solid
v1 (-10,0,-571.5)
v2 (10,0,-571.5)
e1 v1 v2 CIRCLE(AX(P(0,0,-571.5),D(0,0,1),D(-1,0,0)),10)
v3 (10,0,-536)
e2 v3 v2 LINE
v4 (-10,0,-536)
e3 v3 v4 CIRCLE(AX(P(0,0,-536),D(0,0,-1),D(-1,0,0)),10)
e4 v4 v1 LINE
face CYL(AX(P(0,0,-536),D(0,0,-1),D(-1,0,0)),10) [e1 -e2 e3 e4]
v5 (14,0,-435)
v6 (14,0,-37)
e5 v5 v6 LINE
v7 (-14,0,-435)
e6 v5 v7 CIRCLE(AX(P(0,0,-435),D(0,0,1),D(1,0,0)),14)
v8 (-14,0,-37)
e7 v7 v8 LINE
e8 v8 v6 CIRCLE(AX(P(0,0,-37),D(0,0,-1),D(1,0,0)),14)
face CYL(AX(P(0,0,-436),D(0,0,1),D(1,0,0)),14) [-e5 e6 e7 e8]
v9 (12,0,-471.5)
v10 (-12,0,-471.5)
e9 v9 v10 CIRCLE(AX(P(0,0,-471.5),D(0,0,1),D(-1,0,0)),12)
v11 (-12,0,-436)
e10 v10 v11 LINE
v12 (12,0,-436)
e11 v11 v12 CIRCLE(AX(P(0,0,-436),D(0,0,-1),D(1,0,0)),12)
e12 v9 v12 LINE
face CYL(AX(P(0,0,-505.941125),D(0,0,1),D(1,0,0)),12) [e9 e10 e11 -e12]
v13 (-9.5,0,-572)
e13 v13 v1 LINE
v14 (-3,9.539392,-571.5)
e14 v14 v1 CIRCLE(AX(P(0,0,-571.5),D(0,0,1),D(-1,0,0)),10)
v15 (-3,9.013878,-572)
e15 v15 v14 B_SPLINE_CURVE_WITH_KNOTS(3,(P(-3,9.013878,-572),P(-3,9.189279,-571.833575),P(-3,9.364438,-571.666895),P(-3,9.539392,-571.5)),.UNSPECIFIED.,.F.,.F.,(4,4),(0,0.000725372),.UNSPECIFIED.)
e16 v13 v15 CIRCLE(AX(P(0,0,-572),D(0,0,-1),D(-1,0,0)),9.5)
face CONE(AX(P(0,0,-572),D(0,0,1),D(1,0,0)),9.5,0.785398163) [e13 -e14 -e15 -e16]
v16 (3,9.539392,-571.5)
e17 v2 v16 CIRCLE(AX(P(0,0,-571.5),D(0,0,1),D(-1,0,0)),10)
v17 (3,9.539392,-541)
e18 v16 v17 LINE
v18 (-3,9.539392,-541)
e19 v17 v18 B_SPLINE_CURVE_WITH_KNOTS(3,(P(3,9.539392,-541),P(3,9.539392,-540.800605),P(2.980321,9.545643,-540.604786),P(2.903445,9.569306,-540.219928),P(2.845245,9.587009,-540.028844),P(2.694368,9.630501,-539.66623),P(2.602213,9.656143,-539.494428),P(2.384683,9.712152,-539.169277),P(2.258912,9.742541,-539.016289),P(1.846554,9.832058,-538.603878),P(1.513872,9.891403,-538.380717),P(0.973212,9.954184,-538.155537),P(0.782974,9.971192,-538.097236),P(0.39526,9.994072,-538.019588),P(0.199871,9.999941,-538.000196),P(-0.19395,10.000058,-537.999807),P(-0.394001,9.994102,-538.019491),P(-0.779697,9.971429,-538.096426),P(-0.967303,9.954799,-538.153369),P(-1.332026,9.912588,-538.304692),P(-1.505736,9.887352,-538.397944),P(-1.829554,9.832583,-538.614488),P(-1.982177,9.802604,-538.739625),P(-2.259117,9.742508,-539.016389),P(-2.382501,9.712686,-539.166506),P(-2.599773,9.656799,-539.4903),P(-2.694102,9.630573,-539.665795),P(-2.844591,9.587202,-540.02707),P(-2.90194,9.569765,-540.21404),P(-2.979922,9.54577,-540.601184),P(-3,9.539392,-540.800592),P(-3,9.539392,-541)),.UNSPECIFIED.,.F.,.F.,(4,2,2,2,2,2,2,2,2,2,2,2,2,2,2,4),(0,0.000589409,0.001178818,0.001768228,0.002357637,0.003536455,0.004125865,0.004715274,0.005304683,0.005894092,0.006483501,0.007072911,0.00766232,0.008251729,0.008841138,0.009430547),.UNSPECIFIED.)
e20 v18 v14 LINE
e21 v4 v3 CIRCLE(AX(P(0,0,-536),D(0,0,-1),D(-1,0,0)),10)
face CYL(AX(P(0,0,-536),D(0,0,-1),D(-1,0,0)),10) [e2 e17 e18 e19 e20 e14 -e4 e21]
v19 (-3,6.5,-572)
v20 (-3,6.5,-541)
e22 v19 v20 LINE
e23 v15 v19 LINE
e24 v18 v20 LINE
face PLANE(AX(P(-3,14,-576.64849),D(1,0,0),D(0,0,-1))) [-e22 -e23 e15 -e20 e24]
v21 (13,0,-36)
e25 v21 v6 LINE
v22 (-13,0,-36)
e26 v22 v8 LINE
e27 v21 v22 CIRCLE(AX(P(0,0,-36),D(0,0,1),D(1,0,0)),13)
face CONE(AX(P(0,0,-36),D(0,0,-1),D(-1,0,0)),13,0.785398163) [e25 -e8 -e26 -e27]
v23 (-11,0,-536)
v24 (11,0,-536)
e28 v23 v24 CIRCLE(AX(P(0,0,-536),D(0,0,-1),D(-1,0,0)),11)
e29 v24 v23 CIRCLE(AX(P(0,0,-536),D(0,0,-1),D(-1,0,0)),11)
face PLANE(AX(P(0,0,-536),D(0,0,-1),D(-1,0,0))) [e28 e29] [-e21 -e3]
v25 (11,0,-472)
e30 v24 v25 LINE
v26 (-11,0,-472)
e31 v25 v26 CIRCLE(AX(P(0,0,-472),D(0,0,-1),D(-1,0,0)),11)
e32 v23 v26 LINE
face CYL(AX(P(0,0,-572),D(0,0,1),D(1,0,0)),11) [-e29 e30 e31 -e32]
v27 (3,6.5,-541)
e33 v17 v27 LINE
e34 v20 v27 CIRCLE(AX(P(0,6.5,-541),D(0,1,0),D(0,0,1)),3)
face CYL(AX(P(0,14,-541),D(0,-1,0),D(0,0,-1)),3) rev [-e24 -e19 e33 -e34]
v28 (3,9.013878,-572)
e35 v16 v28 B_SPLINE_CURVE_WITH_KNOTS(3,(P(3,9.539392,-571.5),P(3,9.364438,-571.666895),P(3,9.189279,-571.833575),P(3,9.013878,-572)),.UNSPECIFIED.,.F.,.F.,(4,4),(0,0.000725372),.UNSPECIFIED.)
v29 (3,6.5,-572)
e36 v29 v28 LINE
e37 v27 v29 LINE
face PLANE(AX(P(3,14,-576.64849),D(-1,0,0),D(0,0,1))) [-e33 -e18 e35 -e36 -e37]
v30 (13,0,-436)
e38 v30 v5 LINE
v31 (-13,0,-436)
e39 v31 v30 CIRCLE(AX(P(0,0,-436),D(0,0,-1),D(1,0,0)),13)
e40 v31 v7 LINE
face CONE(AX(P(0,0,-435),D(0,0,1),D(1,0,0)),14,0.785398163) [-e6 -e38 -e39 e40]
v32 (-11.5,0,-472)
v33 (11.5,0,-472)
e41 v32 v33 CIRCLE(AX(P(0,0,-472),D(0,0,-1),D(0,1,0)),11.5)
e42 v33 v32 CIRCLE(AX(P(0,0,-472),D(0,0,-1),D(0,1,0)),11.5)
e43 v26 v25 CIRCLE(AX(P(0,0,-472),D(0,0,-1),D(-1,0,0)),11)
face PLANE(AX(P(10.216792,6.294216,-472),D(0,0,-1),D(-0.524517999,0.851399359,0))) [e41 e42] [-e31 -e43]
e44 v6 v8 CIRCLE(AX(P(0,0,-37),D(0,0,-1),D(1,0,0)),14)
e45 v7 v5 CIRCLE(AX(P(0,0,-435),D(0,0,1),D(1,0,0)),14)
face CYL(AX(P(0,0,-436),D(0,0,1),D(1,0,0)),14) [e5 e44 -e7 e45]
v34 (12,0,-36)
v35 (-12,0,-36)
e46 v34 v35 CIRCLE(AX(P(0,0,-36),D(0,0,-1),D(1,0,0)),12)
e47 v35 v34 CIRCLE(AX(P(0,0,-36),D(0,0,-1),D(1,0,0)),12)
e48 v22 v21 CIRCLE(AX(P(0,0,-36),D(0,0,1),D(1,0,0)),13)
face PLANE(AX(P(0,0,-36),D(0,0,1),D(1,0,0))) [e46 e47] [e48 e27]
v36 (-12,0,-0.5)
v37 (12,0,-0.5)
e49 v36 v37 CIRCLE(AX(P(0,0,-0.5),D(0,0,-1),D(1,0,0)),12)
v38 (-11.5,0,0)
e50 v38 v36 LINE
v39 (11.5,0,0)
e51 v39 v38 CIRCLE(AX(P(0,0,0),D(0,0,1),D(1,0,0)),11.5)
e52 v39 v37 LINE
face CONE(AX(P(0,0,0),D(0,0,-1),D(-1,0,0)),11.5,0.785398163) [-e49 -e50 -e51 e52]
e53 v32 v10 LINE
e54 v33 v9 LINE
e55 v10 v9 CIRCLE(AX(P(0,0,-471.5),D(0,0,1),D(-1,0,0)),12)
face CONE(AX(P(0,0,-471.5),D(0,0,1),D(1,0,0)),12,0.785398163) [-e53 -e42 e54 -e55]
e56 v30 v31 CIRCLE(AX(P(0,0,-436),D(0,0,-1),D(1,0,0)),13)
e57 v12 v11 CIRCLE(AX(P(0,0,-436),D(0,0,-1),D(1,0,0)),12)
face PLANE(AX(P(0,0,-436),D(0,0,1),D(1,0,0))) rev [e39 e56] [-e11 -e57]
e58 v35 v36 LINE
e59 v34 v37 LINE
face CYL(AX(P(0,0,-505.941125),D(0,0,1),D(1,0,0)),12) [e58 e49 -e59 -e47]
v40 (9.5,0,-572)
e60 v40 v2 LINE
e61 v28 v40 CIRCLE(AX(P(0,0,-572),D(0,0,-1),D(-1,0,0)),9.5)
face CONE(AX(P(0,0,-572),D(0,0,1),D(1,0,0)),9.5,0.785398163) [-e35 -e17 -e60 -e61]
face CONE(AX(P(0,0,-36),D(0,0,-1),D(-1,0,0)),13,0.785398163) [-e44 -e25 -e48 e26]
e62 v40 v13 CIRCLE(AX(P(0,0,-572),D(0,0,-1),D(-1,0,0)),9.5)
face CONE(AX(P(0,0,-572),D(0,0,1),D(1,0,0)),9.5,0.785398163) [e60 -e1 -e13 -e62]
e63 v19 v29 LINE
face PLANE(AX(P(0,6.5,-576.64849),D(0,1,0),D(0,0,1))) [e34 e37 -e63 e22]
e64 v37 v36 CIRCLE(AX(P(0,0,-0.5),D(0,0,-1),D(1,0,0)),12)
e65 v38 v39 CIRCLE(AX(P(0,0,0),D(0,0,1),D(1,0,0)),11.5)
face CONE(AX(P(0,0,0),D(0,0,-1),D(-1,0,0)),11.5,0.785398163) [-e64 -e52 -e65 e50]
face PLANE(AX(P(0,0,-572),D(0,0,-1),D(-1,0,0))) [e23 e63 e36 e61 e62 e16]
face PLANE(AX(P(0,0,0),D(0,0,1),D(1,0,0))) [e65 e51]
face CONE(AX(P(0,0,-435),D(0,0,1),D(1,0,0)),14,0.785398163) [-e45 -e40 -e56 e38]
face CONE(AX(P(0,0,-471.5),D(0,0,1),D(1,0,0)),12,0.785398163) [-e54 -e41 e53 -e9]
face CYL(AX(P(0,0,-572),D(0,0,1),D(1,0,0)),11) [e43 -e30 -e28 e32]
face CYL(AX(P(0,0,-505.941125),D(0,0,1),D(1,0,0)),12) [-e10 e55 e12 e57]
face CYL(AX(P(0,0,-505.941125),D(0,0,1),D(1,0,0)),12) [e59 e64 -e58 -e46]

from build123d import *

# Parameters (mm, degrees)
SKETCH1_R           = 12
BOSS_EXTRUDE1_DEPTH = 472
SKETCH2_R           = 11
BOSS_EXTRUDE2_DEPTH = 100
SKETCH4_R           = 14
BOSS_EXTRUDE3_DEPTH = 400
CHAMFER1_SIZE       = 1
CHAMFER2_SIZE       = 0.5
CHAMFER3_SIZE       = 0.5
SKETCH5_R           = 20
SKETCH5_R_2         = 10
CUT_EXTRUDE1_DEPTH  = 36
CUT_EXTRUDE2_DEPTH  = 573.538426658
CHAMFER4_SIZE       = 0.5


with BuildPart() as part:
    # Sketch1 → Boss-Extrude1 (new body)
    with BuildSketch(Plane.XY):
        Circle(SKETCH1_R)
    extrude(amount=-BOSS_EXTRUDE1_DEPTH)

    # Sketch2 → Boss-Extrude2 (add)
    with BuildSketch(Plane(origin=(0, 0, -472), x_dir=(-1, 0, 0), z_dir=(0, 0, -1))):
        Circle(SKETCH2_R)
    extrude(amount=BOSS_EXTRUDE2_DEPTH)

    # Sketch4 → Boss-Extrude3 (add)
    with BuildSketch(Plane.XY.offset(-36)):
        Circle(SKETCH4_R)
    extrude(amount=-BOSS_EXTRUDE3_DEPTH)

    # Chamfer1
    chamfer1_edges = [part.edges().sort_by_distance(p)[0] for p in [
        (-14, 0, -36),
        (-14, 0, -436),
    ]]
    chamfer(chamfer1_edges, length=CHAMFER1_SIZE)

    # Chamfer2
    chamfer2_edges = [part.edges().sort_by_distance(p)[0] for p in [
        (-12, 0, 0),
    ]]
    chamfer(chamfer2_edges, length=CHAMFER2_SIZE)

    # Chamfer3
    chamfer3_edges = [part.edges().sort_by_distance(p)[0] for p in [
        (-12, 0, -472),
    ]]
    chamfer(chamfer3_edges, length=CHAMFER3_SIZE)

    # Sketch5 → Cut-Extrude1 (cut)
    with BuildSketch(Plane(origin=(0, 0, -572), x_dir=(-1, 0, 0), z_dir=(0, 0, -1))):
        Circle(SKETCH5_R)
        Circle(SKETCH5_R_2, mode=Mode.SUBTRACT)
    extrude(amount=-CUT_EXTRUDE1_DEPTH, mode=Mode.SUBTRACT)

    # Sketch6 → Cut-Extrude2 (cut, through all)
    with BuildSketch(Plane(origin=(0, 6.5, 0), x_dir=(1, 0, 0), z_dir=(0, 1, 0))):
        with BuildLine():
            Line((3, 576.648489628), (3, 541))
            ThreePointArc((3, 541), (0, 538), (-3, 541))
            Line((-3, 541), (-3, 576.648489628))
            ThreePointArc((-3, 576.648489628), (0, 579.648489628), (3, 576.648489628))
        make_face()
    extrude(amount=CUT_EXTRUDE2_DEPTH, mode=Mode.SUBTRACT)

    # Chamfer4
    chamfer4_edges = [part.edges().sort_by_distance(p)[0] for p in [
        (5.916079783, -8.062257748, -572),
    ]]
    chamfer(chamfer4_edges, length=CHAMFER4_SIZE)


solid = part.part
